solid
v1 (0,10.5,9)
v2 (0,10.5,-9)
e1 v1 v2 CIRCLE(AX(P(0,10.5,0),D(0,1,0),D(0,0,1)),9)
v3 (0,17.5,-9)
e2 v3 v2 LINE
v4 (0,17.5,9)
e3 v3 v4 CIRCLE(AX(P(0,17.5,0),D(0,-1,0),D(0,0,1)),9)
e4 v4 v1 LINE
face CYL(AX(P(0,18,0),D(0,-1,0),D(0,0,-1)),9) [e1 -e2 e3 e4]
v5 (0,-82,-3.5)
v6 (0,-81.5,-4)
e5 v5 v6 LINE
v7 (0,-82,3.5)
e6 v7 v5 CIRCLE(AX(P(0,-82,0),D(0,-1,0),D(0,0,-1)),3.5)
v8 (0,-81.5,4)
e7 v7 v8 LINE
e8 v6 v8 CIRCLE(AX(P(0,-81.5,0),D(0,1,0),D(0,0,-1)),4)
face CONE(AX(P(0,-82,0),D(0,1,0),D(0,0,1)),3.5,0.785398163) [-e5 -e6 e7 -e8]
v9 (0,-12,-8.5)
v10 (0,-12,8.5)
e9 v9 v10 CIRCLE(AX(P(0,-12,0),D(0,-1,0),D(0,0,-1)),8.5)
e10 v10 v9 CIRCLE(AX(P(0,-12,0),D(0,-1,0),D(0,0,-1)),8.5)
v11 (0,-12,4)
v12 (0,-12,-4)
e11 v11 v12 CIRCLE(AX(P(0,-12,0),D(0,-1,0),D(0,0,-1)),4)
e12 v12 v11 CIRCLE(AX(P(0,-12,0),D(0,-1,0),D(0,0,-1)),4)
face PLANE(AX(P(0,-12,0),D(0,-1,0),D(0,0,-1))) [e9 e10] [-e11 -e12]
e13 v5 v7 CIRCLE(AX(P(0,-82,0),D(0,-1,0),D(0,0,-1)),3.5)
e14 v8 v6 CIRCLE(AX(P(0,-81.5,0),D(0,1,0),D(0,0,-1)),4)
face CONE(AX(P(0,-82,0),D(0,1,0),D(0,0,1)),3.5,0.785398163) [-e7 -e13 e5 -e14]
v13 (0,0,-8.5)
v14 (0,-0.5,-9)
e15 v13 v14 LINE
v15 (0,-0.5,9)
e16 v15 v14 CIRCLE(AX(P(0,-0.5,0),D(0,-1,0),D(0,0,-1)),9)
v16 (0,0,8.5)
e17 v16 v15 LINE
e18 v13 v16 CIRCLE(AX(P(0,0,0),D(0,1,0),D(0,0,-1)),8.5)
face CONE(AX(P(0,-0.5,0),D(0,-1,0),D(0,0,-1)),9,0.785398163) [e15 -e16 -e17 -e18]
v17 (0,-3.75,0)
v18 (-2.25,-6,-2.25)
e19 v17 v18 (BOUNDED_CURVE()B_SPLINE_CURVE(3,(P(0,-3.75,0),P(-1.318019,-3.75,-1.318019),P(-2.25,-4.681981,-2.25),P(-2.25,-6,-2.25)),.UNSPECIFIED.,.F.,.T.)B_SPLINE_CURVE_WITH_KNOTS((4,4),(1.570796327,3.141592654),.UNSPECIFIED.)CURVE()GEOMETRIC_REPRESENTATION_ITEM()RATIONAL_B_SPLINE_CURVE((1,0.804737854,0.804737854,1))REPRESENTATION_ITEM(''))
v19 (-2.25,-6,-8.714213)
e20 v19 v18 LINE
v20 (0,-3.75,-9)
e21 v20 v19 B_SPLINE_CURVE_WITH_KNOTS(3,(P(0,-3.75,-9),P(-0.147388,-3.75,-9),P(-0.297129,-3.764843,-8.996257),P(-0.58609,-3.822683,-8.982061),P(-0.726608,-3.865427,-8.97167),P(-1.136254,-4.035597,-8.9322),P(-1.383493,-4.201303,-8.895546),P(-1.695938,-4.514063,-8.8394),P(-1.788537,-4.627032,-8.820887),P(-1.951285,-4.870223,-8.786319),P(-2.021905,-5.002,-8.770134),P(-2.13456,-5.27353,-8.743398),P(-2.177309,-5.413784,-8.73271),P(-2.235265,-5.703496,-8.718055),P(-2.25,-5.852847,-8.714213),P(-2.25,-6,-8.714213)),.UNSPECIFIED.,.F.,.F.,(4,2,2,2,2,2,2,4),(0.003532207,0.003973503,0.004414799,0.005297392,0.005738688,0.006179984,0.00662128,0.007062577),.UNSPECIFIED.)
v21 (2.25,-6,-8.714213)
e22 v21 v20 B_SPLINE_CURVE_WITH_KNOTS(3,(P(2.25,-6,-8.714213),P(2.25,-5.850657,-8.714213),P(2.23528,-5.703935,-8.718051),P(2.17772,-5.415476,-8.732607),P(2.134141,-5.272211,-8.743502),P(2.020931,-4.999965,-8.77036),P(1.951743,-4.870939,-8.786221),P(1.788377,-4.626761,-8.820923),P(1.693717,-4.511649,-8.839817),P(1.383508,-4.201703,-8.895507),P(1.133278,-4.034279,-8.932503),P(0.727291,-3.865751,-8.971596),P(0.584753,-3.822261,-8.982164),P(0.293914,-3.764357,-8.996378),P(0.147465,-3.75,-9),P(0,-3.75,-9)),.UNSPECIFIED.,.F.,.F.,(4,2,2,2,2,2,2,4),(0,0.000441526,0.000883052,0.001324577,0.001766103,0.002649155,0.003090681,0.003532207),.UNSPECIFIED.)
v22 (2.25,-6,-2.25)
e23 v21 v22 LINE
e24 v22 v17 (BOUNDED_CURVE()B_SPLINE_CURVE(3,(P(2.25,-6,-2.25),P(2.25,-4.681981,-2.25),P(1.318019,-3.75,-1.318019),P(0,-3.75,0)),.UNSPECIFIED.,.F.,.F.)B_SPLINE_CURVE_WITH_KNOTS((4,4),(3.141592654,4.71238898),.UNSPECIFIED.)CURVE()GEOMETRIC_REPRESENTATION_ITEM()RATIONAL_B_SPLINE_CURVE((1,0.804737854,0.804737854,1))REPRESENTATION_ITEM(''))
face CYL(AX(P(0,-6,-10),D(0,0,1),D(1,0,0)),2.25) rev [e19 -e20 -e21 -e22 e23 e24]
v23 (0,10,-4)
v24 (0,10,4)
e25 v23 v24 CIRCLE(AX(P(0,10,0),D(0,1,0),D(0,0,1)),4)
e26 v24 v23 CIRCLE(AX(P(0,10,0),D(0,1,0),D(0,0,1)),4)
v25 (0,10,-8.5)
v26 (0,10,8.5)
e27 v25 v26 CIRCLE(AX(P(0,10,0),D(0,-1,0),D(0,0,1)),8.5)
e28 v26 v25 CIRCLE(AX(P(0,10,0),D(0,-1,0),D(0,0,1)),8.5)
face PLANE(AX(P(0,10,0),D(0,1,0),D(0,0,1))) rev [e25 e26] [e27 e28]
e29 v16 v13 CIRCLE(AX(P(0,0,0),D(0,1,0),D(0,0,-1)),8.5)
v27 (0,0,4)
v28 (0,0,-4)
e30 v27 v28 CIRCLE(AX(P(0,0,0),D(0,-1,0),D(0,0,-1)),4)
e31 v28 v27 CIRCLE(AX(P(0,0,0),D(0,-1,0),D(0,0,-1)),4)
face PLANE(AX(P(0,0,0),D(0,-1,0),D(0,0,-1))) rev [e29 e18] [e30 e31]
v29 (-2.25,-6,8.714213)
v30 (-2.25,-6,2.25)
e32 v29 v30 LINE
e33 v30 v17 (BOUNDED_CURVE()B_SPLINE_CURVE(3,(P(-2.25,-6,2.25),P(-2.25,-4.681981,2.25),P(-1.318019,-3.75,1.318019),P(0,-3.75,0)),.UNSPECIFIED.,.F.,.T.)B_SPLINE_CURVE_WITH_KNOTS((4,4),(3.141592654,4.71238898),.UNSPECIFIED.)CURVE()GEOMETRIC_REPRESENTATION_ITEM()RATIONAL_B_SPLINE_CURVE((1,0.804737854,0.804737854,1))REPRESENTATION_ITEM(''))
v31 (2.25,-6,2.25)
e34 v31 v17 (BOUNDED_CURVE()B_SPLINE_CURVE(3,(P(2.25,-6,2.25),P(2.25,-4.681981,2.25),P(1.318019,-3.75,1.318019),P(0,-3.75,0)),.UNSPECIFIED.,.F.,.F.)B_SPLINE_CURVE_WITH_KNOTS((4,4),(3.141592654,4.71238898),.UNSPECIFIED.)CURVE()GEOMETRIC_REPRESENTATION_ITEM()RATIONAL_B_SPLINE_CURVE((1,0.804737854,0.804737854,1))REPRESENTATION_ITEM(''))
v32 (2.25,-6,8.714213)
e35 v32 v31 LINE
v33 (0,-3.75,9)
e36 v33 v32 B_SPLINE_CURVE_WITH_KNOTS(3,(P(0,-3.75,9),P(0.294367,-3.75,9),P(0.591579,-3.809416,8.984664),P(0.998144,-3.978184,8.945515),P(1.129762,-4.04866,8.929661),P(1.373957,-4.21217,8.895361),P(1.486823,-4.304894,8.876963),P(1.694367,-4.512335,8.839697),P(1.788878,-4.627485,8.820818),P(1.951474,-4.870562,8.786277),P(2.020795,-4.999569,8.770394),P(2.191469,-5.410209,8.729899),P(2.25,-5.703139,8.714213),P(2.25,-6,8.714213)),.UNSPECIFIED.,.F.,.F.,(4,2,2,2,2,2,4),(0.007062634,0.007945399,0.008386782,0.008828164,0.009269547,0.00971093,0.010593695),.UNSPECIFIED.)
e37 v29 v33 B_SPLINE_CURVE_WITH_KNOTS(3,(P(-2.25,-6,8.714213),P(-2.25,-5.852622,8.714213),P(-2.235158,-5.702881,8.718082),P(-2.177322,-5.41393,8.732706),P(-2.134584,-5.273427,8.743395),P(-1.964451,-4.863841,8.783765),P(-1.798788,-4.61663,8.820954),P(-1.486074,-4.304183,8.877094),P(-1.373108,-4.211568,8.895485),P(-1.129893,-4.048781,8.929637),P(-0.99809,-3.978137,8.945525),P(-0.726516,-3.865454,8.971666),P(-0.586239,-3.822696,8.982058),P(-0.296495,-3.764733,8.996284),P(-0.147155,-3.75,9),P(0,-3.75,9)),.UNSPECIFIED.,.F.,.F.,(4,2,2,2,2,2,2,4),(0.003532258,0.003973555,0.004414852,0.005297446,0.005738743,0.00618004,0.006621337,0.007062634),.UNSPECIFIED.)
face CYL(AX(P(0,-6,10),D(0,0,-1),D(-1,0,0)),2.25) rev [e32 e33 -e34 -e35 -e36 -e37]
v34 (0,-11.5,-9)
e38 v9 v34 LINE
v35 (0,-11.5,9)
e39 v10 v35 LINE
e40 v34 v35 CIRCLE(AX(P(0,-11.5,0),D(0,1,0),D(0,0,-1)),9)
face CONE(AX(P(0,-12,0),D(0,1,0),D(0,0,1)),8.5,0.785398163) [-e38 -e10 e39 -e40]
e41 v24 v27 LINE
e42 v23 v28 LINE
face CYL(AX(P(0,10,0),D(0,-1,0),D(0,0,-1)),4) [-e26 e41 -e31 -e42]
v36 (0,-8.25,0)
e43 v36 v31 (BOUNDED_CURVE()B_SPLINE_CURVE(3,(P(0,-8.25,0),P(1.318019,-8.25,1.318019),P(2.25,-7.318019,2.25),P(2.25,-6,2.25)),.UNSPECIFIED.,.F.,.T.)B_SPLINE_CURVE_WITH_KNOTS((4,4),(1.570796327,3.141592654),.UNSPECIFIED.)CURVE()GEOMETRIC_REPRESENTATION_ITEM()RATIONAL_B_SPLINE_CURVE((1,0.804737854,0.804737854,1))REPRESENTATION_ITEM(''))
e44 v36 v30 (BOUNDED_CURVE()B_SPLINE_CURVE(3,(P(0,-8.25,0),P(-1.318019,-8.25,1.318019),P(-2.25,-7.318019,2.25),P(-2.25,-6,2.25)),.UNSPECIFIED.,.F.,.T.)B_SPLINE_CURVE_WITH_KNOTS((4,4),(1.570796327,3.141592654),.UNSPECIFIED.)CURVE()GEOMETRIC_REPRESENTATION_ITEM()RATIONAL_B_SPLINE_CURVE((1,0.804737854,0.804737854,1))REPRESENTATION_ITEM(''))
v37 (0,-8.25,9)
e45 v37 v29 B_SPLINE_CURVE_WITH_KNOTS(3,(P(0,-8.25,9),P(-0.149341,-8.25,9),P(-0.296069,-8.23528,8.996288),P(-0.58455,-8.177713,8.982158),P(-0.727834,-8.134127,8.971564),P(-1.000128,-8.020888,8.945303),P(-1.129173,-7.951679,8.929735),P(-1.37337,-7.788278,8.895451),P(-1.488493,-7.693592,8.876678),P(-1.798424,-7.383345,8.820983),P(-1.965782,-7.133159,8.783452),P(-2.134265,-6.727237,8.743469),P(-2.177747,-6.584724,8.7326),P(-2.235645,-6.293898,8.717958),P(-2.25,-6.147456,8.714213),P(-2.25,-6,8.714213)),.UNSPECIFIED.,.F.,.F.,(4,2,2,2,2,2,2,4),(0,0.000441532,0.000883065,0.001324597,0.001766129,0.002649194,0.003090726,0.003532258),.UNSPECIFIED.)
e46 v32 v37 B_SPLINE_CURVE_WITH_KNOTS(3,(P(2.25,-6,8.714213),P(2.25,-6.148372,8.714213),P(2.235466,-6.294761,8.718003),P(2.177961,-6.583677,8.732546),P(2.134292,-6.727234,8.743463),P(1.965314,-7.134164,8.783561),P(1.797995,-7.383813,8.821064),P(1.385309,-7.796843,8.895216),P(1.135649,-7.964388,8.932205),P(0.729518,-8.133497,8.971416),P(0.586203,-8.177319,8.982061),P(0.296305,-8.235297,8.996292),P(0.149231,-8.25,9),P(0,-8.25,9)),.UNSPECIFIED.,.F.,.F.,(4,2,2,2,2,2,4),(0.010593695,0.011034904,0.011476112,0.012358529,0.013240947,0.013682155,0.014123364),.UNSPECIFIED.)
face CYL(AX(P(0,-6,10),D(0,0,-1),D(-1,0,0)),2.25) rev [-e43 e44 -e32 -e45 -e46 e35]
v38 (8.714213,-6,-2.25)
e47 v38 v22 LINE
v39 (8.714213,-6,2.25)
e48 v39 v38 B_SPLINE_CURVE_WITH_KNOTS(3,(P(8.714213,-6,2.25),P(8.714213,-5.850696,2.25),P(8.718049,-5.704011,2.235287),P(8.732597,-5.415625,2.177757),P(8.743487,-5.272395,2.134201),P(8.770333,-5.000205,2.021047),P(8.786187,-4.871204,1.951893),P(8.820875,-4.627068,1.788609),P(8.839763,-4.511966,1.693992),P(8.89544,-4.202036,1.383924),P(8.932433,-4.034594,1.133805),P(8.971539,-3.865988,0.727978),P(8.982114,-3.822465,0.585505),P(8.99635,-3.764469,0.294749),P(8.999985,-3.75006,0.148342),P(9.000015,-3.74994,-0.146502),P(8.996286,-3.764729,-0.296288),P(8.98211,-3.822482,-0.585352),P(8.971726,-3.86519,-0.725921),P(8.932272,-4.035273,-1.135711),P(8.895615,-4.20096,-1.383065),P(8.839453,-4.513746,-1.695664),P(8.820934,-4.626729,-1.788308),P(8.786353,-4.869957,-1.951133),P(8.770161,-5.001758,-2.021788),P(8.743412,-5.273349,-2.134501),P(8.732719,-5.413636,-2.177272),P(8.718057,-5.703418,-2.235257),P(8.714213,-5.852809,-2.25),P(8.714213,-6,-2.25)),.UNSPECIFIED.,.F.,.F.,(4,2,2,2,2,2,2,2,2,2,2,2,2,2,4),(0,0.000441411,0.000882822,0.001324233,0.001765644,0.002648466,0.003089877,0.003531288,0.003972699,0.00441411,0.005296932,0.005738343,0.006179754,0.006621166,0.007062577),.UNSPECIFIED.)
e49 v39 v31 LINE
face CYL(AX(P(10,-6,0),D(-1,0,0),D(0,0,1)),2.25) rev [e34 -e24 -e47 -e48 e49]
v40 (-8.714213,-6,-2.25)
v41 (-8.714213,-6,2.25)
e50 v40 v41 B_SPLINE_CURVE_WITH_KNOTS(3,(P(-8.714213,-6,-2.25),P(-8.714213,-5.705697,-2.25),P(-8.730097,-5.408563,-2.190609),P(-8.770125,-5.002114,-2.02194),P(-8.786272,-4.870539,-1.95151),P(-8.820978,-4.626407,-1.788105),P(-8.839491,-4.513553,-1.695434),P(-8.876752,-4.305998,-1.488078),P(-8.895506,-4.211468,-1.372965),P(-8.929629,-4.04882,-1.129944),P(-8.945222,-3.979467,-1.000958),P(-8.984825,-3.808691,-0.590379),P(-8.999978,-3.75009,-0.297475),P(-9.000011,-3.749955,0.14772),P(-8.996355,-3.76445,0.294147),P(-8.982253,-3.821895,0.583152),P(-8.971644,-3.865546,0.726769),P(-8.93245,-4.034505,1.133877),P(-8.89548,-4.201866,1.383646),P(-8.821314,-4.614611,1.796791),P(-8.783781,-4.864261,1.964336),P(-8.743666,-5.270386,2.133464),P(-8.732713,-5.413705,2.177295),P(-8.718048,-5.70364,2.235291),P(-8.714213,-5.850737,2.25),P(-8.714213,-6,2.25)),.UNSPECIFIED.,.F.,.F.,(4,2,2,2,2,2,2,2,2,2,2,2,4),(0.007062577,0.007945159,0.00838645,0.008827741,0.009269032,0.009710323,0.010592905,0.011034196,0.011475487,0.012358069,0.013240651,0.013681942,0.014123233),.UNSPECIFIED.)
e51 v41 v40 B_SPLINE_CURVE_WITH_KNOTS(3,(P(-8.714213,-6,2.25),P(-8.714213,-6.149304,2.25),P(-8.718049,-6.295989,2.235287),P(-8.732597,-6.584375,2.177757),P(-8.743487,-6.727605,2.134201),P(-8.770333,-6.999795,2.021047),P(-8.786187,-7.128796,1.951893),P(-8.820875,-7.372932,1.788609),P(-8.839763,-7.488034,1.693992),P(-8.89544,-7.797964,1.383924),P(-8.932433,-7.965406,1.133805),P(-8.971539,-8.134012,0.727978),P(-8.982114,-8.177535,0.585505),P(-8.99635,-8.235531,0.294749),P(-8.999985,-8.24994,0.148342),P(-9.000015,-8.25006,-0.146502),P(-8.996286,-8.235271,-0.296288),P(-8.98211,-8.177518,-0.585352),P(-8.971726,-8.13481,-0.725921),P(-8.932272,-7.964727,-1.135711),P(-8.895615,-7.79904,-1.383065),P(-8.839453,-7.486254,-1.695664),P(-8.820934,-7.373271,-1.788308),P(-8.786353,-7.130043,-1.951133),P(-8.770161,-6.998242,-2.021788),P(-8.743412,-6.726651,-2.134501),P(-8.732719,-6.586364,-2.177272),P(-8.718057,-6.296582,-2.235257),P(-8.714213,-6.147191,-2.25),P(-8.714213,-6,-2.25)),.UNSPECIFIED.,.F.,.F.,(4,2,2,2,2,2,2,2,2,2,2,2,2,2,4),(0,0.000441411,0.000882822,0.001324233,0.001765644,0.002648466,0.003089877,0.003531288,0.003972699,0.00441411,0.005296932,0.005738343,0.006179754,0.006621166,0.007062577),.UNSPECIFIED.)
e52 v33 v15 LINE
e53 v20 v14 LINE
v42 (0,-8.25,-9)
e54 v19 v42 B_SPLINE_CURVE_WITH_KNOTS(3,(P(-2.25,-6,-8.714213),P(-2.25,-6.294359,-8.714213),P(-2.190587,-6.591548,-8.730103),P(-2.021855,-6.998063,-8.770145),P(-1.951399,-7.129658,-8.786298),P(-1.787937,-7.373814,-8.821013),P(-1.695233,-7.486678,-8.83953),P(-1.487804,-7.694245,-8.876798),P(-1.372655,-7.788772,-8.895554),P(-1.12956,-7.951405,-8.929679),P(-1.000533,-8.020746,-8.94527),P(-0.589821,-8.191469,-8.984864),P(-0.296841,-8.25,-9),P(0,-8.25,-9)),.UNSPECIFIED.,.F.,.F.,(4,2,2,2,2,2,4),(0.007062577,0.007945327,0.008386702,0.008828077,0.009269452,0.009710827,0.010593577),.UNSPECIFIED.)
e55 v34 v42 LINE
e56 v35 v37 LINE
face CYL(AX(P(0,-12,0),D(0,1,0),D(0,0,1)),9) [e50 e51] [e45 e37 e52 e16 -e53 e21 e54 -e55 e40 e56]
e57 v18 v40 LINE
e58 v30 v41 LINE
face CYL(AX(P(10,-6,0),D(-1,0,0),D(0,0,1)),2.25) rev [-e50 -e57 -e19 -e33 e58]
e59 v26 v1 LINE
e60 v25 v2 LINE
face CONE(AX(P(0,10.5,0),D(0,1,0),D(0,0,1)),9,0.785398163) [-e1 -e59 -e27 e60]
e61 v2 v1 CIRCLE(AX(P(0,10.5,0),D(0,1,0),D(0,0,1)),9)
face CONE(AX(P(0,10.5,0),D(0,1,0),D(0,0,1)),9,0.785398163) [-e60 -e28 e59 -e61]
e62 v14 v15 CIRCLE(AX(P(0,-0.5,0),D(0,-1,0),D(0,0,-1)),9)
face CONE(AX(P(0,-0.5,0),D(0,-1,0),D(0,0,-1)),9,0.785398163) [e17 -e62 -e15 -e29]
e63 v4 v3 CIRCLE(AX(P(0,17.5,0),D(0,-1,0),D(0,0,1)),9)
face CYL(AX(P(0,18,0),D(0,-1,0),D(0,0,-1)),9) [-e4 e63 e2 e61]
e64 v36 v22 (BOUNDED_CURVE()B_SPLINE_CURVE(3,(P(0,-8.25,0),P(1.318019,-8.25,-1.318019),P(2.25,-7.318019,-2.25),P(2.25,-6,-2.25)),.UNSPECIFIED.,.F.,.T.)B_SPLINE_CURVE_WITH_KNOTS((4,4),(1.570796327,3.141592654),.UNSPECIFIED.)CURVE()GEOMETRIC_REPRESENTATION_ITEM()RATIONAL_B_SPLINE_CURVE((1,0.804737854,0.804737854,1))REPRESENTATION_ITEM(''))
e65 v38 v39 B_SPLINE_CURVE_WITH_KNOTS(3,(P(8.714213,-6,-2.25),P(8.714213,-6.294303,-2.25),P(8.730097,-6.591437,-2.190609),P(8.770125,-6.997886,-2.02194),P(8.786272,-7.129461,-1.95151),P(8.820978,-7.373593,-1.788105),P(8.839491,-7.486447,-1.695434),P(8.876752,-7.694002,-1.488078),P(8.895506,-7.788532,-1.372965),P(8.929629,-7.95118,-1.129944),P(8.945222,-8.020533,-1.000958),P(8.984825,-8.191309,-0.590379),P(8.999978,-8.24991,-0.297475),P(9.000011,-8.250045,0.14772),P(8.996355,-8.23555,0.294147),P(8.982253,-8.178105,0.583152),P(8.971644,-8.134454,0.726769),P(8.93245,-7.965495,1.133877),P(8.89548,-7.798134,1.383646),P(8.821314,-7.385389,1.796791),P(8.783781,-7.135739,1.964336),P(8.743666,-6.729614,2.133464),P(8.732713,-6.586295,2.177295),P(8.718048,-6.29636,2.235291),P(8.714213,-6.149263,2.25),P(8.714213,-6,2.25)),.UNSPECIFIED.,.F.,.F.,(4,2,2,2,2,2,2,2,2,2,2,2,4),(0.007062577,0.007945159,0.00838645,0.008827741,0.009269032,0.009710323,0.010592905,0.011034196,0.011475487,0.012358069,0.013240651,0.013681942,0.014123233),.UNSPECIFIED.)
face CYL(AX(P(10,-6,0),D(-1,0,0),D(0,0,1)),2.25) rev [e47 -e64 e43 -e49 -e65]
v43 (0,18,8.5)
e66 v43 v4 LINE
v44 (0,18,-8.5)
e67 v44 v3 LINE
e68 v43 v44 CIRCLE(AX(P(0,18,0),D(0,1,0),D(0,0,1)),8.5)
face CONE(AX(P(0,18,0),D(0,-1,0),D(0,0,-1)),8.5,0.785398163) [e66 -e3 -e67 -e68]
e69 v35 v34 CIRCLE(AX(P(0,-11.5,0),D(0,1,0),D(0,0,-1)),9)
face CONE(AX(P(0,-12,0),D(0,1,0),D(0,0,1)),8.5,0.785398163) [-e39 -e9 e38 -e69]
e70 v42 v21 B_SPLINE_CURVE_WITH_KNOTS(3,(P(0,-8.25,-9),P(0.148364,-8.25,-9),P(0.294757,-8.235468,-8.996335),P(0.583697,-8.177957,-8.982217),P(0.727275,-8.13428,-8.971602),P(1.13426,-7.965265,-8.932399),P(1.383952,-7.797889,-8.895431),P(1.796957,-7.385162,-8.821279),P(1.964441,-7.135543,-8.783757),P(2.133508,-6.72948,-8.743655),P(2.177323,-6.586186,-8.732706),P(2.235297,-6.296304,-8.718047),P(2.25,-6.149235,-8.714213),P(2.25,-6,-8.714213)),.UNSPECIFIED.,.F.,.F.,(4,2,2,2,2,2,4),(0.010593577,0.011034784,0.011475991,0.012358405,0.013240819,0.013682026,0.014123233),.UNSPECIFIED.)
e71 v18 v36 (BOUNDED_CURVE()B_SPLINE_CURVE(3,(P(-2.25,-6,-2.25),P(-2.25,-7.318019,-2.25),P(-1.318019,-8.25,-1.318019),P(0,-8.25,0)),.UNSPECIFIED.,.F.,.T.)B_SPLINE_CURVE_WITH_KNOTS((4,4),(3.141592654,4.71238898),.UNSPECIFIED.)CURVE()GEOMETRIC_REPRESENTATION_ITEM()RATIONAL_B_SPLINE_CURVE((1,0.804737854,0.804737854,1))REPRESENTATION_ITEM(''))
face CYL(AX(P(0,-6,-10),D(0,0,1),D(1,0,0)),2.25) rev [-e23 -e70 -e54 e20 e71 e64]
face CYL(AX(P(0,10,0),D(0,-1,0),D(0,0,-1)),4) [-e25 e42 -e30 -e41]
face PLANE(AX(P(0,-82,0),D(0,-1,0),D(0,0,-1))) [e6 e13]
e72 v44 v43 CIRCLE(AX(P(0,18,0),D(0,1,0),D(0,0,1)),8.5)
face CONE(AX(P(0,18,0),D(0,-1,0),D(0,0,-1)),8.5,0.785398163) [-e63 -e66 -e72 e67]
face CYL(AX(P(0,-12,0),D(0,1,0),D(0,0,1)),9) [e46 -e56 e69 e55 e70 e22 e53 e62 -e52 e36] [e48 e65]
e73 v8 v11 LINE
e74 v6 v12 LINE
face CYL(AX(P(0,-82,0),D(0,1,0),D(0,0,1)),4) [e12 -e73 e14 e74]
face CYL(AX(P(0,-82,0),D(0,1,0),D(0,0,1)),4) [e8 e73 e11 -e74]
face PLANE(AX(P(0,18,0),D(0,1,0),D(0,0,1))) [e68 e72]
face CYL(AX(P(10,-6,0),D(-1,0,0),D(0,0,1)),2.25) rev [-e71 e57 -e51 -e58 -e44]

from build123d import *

# Parameters (mm, degrees)
SKETCH1_R           = 4
BOSS_EXTRUDE1_DEPTH = 10
SKETCH2_R           = 9
BOSS_EXTRUDE2_DEPTH = 8
BOSS_EXTRUDE3_START = 12
SKETCH3_R           = 9
BOSS_EXTRUDE3_DEPTH = 12
BOSS_EXTRUDE4_START = 70
SKETCH4_R           = 4
BOSS_EXTRUDE4_DEPTH = 70
CHAMFER1_SIZE       = 0.5
SKETCH6_R           = 2.25
CUT_EXTRUDE2_DEPTH  = 10
CIRPATTERN1_COUNT   = 4
CHAMFER2_SIZE       = 0.5


with BuildPart() as part:
    # Sketch1 → Boss-Extrude1 (new body)
    with BuildSketch(Plane(origin=(0, 0, 0), x_dir=(1, 0, 0), z_dir=(0, 1, 0))):
        with Locations(Location((0, 0, 0), (0, 0, 270))):
            Circle(SKETCH1_R)
    extrude(amount=BOSS_EXTRUDE1_DEPTH)

    # Sketch2 → Boss-Extrude2 (add)
    with BuildSketch(Plane(origin=(0, 10, 0), x_dir=(1, 0, 0), z_dir=(0, 1, 0))):
        with Locations(Location((0, 0, 0), (0, 0, 270))):
            Circle(SKETCH2_R)
    extrude(amount=BOSS_EXTRUDE2_DEPTH)

    # Sketch3 → Boss-Extrude3 (add)
    with BuildSketch(Plane.XZ.offset(BOSS_EXTRUDE3_START)):
        with Locations(Location((0, 0, 0), (0, 0, 90))):
            Circle(SKETCH3_R)
    extrude(amount=-BOSS_EXTRUDE3_DEPTH)

    # Sketch4 → Boss-Extrude4 (add)
    with BuildSketch(Plane.XZ.offset(12).offset(BOSS_EXTRUDE4_START)):
        with Locations(Location((0, 0, 0), (0, 0, 270))):
            Circle(SKETCH4_R)
    extrude(amount=-BOSS_EXTRUDE4_DEPTH)

    # Chamfer1
    chamfer1_edges = [part.edges().sort_by_distance(p)[0] for p in [
        (0, -82, 4),
    ]]
    chamfer(chamfer1_edges, length=CHAMFER1_SIZE)

    # Sketch6 → Cut-Extrude2 (cut)
    with BuildSketch(Plane.XY):
        with Locations((0, -6)):
            Circle(SKETCH6_R)
    cut_extrude2 = extrude(amount=-CUT_EXTRUDE2_DEPTH, mode=Mode.SUBTRACT)

    # CirPattern1: Cut-Extrude2 ×4 about axis
    cirpattern1_axis = Axis((0, 18, 0), (0, -1, 0))
    for i in range(1, CIRPATTERN1_COUNT):
        add(cut_extrude2.rotate(cirpattern1_axis, i * 360 / CIRPATTERN1_COUNT), mode=Mode.SUBTRACT)

    # Chamfer2
    chamfer2_edges = [part.edges().sort_by_distance(p)[0] for p in [
        (0, 10, -9),
        (0, 18, -9),
        (0, 0, -9),
        (0, -12, -9),
    ]]
    chamfer(chamfer2_edges, length=CHAMFER2_SIZE)


solid = part.part
